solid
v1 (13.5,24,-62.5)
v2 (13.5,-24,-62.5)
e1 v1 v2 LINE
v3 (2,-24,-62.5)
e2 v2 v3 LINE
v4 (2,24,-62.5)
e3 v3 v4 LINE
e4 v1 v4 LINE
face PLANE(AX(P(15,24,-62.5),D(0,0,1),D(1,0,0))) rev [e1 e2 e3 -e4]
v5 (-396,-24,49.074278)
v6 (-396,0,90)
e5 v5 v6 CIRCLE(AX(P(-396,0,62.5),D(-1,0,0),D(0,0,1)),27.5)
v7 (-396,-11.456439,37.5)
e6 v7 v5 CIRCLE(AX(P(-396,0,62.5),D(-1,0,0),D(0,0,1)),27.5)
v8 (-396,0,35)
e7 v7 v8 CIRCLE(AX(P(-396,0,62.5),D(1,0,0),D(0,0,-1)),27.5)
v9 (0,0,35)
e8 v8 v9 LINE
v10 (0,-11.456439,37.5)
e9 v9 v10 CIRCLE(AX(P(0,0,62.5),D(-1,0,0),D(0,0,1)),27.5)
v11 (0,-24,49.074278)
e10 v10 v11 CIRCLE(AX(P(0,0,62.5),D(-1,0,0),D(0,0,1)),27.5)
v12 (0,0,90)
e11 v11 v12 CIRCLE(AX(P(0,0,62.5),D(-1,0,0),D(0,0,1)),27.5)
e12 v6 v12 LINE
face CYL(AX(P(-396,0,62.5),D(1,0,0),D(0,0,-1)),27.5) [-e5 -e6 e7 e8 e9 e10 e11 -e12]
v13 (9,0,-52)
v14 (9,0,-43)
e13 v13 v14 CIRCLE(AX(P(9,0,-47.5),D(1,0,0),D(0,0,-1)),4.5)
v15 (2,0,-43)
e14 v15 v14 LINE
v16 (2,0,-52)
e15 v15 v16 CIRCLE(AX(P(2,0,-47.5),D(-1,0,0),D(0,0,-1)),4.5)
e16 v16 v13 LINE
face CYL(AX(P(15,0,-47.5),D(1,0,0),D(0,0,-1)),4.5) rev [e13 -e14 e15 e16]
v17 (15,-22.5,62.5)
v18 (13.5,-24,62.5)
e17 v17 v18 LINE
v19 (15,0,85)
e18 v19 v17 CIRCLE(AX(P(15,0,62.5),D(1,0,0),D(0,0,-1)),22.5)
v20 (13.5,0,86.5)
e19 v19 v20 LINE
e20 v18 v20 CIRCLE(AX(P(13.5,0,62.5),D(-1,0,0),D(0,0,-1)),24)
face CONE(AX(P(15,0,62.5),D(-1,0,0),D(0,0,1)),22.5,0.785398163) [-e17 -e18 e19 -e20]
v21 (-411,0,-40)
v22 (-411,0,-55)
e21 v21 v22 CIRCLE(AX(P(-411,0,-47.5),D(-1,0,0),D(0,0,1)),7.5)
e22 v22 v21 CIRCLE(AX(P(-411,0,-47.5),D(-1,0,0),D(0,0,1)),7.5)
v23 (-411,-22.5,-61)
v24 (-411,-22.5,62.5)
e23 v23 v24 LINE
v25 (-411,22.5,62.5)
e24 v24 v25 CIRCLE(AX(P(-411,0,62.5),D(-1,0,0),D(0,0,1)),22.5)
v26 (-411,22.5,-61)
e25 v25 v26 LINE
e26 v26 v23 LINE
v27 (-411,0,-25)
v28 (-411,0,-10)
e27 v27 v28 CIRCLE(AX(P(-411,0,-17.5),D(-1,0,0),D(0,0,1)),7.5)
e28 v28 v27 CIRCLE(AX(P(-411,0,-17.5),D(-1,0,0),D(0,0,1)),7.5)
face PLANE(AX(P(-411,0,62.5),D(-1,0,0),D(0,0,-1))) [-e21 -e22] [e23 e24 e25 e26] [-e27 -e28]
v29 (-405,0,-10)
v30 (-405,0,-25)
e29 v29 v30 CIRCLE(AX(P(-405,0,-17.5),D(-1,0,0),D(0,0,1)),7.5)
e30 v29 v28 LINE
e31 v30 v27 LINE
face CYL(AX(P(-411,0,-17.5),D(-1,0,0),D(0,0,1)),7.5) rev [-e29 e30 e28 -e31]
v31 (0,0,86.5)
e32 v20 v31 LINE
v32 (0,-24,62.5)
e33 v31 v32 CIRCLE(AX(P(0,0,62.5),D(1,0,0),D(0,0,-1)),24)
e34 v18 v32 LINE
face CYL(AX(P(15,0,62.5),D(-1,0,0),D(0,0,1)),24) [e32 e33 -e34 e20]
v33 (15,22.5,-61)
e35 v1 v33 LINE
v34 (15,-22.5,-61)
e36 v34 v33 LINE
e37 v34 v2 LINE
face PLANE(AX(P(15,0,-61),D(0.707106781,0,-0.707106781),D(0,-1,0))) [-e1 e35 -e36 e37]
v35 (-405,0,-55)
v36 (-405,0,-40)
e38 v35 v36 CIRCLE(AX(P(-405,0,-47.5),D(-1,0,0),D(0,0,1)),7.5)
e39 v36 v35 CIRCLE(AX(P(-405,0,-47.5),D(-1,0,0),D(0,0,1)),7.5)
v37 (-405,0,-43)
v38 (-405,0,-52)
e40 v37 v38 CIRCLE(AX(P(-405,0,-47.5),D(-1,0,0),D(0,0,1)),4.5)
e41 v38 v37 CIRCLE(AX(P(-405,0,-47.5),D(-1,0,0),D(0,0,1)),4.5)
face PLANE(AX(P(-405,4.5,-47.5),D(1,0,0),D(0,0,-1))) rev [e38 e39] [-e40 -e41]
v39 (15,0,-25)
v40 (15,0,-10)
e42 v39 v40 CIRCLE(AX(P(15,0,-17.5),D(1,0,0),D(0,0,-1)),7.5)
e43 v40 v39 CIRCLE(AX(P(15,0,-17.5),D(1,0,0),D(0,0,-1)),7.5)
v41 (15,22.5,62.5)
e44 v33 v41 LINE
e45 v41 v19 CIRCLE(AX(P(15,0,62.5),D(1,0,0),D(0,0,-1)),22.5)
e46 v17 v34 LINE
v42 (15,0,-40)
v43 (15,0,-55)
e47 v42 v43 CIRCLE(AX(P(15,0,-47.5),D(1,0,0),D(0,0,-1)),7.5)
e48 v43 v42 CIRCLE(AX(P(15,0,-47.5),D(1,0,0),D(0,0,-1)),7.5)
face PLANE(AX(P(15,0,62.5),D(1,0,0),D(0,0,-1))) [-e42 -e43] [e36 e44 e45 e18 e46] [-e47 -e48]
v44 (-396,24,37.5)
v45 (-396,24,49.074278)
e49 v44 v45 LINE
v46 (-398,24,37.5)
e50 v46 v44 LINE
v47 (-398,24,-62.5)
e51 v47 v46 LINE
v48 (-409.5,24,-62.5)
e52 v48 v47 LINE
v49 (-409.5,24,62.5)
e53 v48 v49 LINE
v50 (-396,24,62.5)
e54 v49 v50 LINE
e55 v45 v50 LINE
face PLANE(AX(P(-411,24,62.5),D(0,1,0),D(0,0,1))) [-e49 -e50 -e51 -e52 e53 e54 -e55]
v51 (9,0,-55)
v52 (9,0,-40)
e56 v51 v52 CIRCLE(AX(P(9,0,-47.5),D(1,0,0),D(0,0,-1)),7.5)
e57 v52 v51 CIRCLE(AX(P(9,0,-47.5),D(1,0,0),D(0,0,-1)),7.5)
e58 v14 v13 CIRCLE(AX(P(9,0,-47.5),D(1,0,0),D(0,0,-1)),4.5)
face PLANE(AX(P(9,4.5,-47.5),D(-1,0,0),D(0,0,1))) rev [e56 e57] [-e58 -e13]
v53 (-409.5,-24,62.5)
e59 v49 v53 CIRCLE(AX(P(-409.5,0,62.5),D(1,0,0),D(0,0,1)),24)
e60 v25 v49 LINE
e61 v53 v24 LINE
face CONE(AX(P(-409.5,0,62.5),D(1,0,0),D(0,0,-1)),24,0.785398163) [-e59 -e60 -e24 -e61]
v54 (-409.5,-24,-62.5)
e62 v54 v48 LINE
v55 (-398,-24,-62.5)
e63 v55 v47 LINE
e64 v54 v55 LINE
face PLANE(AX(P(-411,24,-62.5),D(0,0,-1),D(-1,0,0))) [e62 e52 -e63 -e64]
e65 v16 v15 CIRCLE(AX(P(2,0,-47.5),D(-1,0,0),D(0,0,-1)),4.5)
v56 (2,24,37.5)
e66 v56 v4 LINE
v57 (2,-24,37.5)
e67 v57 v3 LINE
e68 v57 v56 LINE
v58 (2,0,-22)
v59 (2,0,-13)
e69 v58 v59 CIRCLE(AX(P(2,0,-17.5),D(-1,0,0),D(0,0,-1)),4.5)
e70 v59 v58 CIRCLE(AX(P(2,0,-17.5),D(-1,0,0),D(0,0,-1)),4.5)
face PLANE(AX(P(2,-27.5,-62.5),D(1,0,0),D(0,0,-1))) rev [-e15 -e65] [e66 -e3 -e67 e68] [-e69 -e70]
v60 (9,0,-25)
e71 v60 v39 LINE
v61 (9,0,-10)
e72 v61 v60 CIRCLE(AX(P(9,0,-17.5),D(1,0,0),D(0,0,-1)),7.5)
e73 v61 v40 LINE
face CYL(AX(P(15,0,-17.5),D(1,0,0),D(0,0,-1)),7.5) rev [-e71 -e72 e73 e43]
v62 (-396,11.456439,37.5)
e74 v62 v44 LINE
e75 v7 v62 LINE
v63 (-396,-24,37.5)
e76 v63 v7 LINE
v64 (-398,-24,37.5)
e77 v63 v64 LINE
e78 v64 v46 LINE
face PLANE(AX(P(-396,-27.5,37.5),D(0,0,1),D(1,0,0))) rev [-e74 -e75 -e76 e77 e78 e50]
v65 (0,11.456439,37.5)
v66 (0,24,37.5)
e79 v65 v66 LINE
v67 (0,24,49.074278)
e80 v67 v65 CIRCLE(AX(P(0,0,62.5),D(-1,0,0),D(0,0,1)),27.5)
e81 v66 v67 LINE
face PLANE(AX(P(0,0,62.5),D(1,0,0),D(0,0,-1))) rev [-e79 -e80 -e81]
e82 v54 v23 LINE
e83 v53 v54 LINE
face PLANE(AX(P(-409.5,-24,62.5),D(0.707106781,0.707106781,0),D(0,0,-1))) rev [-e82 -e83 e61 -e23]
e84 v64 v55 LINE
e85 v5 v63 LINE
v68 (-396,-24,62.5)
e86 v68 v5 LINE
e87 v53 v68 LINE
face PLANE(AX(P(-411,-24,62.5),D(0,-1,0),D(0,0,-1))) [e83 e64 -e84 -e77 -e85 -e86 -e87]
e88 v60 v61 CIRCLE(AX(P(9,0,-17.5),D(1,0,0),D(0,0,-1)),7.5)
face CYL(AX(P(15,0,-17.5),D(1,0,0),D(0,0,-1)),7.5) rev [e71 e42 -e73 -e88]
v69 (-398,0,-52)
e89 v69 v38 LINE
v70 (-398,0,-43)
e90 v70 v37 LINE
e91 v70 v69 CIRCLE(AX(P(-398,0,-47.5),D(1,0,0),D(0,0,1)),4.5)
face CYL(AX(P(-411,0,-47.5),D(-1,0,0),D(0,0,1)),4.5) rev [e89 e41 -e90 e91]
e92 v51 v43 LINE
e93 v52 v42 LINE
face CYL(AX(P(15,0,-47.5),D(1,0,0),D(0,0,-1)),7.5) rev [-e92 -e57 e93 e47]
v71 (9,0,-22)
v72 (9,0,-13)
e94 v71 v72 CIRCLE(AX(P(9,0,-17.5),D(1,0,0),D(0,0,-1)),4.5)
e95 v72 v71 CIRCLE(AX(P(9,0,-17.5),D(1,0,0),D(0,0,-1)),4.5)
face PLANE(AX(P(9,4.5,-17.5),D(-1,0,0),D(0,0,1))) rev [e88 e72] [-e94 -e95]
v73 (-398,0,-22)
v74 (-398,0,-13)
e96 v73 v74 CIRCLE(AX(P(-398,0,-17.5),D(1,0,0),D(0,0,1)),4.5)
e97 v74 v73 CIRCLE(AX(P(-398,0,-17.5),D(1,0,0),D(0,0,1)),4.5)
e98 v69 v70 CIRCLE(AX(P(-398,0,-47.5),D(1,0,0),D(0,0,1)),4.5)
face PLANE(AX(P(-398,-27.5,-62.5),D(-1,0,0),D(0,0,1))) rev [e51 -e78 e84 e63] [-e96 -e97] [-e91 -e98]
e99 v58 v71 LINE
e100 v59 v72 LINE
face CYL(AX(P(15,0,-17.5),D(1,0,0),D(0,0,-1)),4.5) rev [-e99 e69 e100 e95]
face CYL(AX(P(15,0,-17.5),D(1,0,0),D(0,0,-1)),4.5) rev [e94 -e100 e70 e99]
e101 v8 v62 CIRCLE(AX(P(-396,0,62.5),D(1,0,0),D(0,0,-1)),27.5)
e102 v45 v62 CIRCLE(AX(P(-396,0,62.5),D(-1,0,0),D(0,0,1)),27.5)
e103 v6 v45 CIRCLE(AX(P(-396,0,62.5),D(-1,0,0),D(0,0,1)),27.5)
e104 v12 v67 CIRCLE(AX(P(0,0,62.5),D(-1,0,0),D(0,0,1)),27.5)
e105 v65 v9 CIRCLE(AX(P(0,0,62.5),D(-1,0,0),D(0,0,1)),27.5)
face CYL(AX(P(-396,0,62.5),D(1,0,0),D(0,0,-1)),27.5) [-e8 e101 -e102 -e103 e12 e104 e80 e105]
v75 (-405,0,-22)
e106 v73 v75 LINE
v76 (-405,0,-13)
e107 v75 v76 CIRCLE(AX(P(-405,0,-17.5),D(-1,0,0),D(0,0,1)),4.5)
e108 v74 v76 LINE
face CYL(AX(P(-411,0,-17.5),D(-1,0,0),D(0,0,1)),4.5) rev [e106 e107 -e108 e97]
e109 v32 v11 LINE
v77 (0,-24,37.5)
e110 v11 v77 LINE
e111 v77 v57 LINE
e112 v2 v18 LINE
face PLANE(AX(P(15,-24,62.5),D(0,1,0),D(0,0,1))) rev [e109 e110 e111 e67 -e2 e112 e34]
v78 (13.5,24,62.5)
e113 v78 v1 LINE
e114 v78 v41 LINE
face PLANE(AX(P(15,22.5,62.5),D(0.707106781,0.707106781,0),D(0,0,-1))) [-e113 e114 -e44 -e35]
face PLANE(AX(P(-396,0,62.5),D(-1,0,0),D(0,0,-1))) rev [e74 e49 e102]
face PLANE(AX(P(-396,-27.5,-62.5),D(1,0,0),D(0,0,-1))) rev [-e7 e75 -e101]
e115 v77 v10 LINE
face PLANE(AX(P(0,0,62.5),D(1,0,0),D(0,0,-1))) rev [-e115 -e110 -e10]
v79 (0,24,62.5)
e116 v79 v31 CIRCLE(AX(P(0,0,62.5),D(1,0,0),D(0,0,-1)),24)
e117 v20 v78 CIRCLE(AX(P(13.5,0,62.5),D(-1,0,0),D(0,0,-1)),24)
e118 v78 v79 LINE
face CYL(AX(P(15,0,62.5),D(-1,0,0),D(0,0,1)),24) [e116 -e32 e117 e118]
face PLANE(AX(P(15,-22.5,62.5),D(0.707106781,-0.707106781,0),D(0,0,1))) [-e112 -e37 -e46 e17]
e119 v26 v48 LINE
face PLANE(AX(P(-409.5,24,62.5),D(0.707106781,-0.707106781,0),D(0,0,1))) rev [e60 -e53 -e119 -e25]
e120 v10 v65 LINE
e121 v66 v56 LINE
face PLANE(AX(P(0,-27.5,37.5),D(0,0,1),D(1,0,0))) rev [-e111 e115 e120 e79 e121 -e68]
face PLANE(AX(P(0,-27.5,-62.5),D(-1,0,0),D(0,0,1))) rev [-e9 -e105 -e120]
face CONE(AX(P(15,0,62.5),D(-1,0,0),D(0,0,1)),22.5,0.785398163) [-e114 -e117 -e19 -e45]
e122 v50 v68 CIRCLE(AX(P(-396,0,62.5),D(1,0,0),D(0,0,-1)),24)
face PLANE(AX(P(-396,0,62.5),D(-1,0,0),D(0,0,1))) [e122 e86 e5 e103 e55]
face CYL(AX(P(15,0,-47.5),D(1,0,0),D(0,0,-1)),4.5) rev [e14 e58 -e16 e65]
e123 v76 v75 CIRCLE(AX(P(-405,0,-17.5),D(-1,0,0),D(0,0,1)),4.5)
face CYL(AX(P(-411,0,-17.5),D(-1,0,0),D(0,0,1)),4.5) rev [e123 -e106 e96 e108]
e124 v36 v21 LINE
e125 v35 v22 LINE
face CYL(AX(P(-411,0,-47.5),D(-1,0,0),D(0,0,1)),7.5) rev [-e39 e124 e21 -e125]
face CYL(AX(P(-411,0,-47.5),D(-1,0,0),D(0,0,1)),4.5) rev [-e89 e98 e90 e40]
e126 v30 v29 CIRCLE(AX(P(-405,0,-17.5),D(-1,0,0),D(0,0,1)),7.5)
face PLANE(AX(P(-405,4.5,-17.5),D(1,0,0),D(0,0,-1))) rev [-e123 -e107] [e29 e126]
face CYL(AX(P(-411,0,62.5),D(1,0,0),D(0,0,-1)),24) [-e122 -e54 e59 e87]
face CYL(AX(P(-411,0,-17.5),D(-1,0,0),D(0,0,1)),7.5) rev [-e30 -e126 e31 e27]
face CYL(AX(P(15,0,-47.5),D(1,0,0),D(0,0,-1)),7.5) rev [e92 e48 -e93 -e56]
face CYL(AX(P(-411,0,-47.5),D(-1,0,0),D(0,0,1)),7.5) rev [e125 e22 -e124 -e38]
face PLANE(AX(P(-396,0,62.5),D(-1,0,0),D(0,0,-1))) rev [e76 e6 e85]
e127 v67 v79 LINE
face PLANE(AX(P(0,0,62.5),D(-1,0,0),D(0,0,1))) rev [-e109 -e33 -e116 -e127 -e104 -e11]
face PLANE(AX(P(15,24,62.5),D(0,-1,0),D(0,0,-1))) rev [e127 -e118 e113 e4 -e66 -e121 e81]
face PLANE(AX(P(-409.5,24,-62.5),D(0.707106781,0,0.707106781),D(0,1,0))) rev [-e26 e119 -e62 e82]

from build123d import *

# Parameters (mm, degrees)
EXTRUDE_1_DEPTH            = 15
SKETCH_2_R                 = 27.5
EXTRUDE_2_DEPTH            = 396
HOLE_WIZARD_1_D            = 9
HOLE_WIZARD_1_CBORE_D      = 15
HOLE_WIZARD_1_CBORE_DEPTH  = 6
CHAMFER_1_SIZE             = 1.5
CHAMFER_1_OF_MIRROR_1_SIZE = 1.5
SKETCH_5_W                 = 2
SKETCH_5_H                 = 100
CUT_EXTRUDE_1_DEPTH        = 424.878815229


with BuildPart() as part:
    # 草图1 → 凸台-拉伸1 (new body)
    with BuildSketch(Plane(origin=(0, 0, 0), x_dir=(0, 0, -1), z_dir=(1, 0, 0))):
        with BuildLine():
            Line((-62.5, 24), (62.5, 24))
            Line((62.5, 24), (62.5, -24))
            Line((62.5, -24), (-62.5, -24))
            ThreePointArc((-62.5, -24), (-86.5, 0), (-62.5, 24))
        make_face()
    extrude_1 = extrude(amount=EXTRUDE_1_DEPTH)

    # 草图2 → 凸台-拉伸2 (add)
    with BuildSketch(Plane.ZY):
        with Locations(Location((62.5, 0, 0), (0, 0, 240.777129706))):
            Circle(SKETCH_2_R)
    extrude(amount=EXTRUDE_2_DEPTH)

    # 打孔尺寸(%根据)内六角花形圆柱头螺钉1 (through all)
    with Locations(Plane(origin=(15, 0, 0), x_dir=(0, 0, -1), z_dir=(1, 0, 0))):
        with Locations((17.5, 0), (47.5, 0)):
            hole_wizard_1 = CounterBoreHole(HOLE_WIZARD_1_D / 2, HOLE_WIZARD_1_CBORE_D / 2, HOLE_WIZARD_1_CBORE_DEPTH)

    # 倒角1
    chamfer_1_edges = [part.edges().sort_by_distance(p)[0] for p in [
        (15, 0, 86.5),
        (15, -24, 0),
        (15, 0, -62.5),
        (15, 24, 0),
    ]]
    chamfer(chamfer_1_edges, length=CHAMFER_1_SIZE)

    # 镜向1: 凸台-拉伸1, 打孔尺寸(%根据)内六角花形圆柱头螺钉1 across plane
    add(extrude_1.mirror(Plane.ZY.offset(198)))
    add(hole_wizard_1.mirror(Plane.ZY.offset(198)), mode=Mode.SUBTRACT)

    # 倒角1 of 镜向1
    chamfer_1_of_mirror_1_edges = [part.edges().sort_by_distance(p)[0] for p in [
        (-411, 0, 86.5),
        (-411, -24, 0),
        (-411, 0, -62.5),
        (-411, 24, 0),
    ]]
    chamfer(chamfer_1_of_mirror_1_edges, length=CHAMFER_1_OF_MIRROR_1_SIZE)

    # 草图5 → 切除-拉伸1 (cut, through all)
    with BuildSketch(Plane(origin=(0, 24, 0), x_dir=(1, 0, 0), z_dir=(0, 1, 0))):
        with Locations((-397, 12.5)):
            Rectangle(SKETCH_5_W, SKETCH_5_H)
        with Locations((1, 12.5)):
            Rectangle(SKETCH_5_W, SKETCH_5_H)
    extrude(amount=-CUT_EXTRUDE_1_DEPTH, mode=Mode.SUBTRACT)


solid = part.part
